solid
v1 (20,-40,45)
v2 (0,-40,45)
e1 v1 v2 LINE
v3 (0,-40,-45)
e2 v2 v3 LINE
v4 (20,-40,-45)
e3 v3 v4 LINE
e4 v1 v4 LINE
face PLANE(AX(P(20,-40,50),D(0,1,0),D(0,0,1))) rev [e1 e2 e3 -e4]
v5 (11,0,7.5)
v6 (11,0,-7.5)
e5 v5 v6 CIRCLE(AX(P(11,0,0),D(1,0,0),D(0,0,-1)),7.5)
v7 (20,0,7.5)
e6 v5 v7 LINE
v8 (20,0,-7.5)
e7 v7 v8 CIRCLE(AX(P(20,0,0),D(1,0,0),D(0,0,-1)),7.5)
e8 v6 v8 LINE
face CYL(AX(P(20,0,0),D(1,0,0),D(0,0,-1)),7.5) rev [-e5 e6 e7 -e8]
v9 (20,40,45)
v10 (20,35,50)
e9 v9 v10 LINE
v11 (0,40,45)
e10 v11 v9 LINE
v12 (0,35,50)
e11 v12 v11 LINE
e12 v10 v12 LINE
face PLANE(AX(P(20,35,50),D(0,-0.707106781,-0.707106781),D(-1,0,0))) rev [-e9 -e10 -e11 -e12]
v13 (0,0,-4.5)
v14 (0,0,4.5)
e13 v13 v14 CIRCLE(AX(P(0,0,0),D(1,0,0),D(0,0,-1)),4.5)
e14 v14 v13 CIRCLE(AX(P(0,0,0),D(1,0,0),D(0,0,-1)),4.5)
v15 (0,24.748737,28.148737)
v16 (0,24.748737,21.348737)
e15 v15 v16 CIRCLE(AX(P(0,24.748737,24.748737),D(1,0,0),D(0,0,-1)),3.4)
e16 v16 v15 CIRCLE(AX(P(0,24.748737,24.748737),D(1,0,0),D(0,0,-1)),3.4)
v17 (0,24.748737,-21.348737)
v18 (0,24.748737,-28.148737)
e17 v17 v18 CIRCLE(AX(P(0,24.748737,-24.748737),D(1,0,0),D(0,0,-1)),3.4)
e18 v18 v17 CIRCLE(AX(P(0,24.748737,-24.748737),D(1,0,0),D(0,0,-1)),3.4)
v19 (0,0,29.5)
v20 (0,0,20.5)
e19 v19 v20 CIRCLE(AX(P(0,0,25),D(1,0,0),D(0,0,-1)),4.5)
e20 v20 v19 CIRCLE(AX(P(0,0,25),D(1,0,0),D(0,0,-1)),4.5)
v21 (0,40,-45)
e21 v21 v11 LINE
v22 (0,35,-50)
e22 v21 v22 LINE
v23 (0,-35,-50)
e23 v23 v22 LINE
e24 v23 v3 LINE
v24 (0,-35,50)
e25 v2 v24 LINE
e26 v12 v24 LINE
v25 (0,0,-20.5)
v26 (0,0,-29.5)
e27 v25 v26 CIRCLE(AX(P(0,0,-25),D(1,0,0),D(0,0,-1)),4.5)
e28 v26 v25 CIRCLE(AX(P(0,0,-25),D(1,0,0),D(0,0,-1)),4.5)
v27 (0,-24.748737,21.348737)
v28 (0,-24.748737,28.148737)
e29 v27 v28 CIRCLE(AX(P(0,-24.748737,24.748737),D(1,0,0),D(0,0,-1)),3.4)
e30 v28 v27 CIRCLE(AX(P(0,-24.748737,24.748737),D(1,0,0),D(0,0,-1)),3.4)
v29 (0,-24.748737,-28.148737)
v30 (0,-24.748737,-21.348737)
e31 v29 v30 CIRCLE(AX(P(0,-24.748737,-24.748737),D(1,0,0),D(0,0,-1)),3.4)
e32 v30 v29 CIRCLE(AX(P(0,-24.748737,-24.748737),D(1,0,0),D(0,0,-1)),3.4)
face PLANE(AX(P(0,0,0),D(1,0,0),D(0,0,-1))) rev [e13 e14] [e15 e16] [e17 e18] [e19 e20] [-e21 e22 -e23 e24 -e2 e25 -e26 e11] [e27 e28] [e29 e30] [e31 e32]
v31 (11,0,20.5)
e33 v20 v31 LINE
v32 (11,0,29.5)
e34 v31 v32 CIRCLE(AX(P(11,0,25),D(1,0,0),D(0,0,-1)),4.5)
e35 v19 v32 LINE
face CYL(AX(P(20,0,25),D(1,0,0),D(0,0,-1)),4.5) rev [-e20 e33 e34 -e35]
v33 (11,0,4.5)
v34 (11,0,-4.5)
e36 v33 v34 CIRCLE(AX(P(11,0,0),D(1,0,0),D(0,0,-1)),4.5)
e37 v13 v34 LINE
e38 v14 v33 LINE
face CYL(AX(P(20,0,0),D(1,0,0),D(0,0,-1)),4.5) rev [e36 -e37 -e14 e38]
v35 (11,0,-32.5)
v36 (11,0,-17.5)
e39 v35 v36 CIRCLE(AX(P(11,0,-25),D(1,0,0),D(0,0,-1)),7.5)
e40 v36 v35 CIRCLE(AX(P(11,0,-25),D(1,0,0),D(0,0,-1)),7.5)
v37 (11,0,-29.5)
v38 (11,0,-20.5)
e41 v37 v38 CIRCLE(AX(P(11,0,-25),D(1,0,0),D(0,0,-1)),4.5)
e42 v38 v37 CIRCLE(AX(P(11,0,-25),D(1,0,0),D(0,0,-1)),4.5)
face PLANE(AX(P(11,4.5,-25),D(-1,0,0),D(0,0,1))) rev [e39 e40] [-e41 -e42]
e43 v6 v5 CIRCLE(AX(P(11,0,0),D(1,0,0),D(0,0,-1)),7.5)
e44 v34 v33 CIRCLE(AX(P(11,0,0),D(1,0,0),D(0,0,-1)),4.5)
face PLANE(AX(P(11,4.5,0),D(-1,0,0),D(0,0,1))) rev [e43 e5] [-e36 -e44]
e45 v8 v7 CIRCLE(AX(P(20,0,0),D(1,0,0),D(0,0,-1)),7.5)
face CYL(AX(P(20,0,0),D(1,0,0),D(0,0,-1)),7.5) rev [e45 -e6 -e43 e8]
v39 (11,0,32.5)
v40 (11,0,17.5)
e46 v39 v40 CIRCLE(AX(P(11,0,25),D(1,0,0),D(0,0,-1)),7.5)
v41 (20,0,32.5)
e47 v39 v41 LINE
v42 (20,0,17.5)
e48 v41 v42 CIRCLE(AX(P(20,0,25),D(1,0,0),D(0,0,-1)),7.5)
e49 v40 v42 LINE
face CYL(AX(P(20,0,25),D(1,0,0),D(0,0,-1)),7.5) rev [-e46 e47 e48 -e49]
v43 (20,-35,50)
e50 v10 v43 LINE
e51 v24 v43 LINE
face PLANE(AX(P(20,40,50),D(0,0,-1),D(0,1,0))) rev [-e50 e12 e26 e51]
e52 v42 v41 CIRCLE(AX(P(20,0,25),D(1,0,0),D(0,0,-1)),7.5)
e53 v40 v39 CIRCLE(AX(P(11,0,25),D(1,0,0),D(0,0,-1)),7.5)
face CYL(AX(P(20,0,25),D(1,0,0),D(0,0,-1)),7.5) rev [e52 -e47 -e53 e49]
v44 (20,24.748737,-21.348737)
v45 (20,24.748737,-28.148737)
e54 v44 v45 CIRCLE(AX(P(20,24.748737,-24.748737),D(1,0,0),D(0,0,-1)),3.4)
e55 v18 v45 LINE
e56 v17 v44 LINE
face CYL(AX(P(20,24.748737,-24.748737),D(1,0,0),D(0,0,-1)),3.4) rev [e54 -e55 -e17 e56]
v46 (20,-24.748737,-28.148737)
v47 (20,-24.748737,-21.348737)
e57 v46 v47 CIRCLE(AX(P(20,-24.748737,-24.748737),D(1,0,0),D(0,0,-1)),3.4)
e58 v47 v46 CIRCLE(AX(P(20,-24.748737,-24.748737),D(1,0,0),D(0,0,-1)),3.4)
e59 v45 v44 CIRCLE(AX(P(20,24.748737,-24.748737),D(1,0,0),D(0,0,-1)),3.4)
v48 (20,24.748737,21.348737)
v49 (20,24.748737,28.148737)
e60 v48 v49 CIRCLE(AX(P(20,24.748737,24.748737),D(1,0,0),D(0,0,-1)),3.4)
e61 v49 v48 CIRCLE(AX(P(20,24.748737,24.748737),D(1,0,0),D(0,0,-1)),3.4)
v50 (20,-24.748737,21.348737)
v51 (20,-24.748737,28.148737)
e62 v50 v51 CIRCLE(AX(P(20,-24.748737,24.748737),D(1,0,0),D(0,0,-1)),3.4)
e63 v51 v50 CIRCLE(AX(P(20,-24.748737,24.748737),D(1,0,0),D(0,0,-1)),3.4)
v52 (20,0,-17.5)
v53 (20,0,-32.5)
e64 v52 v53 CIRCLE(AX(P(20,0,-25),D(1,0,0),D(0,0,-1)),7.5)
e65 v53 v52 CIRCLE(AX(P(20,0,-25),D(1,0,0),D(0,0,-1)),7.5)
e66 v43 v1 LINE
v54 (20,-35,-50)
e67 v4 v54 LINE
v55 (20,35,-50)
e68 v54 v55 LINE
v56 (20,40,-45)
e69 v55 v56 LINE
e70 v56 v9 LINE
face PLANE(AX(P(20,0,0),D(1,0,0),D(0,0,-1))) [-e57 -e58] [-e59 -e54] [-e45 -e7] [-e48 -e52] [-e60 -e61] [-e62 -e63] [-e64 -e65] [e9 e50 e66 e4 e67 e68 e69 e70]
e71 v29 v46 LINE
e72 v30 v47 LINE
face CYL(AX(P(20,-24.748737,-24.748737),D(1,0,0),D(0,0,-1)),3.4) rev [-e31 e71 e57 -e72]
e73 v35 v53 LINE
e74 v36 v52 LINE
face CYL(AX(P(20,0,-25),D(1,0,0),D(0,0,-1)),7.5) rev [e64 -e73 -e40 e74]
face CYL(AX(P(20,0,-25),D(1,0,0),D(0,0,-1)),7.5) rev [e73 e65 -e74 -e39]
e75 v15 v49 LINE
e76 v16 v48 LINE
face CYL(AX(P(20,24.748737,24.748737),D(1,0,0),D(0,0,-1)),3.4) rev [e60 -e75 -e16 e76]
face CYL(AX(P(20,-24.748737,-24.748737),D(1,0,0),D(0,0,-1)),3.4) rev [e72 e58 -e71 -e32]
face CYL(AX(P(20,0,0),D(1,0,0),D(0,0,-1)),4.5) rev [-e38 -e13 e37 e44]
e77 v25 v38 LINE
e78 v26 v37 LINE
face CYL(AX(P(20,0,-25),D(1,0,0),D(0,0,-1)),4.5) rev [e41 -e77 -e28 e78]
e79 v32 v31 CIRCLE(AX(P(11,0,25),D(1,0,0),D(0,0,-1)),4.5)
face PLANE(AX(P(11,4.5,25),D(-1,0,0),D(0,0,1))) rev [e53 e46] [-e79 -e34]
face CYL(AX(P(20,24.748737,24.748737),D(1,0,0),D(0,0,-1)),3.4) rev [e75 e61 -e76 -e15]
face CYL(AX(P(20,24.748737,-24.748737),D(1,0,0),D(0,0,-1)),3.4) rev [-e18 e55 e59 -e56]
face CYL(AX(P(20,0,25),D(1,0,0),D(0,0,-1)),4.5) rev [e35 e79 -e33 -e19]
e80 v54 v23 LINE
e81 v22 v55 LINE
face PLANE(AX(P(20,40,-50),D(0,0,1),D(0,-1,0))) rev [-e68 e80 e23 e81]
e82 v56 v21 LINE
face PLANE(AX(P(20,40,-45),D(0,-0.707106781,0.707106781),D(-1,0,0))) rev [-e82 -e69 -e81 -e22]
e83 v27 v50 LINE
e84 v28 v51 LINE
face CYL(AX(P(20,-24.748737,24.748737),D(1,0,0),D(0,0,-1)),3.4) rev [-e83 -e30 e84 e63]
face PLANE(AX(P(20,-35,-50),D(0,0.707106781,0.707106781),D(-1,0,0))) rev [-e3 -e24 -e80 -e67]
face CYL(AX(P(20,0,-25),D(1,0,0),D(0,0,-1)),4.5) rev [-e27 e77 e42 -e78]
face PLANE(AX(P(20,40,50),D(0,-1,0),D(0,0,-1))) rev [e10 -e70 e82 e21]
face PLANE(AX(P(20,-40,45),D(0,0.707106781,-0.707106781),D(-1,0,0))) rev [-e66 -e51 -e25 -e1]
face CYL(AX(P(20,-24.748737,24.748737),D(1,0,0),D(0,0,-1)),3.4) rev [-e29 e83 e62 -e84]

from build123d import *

# Parameters (mm, degrees)
SKETCH_1_W                = 100
SKETCH_1_H                = 80
EXTRUDE_1_DEPTH           = 20
HOLE_WIZARD_M8_1_D        = 6.8
HOLE_WIZARD_1_D           = 9
HOLE_WIZARD_1_CBORE_D     = 15
HOLE_WIZARD_1_CBORE_DEPTH = 9
CHAMFER_1_SIZE            = 5


with BuildPart() as part:
    # 草图1 → 凸台-拉伸1 (new body)
    with BuildSketch(Plane(origin=(0, 0, 0), x_dir=(0, 0, -1), z_dir=(1, 0, 0))):
        Rectangle(SKETCH_1_W, SKETCH_1_H)
    extrude(amount=EXTRUDE_1_DEPTH)

    # M8 螺纹孔1 (through all)
    with Locations(Plane(origin=(20, 0, 0), x_dir=(0, 0, -1), z_dir=(1, 0, 0))):
        with Locations((-24.748737342, 24.748737342), (24.748737342, 24.748737342), (24.748737342, -24.748737342), (-24.748737342, -24.748737342)):
            Hole(HOLE_WIZARD_M8_1_D / 2)

    # 打孔尺寸(%根据)内六角圆柱头螺钉的类型1 (through all)
    with Locations(Plane(origin=(20, 0, 0), x_dir=(0, 0, -1), z_dir=(1, 0, 0))):
        with Locations((-25, 0), (0, 0), (25, 0)):
            CounterBoreHole(HOLE_WIZARD_1_D / 2, HOLE_WIZARD_1_CBORE_D / 2, HOLE_WIZARD_1_CBORE_DEPTH)

    # 倒角1
    chamfer_1_edges = [part.edges().sort_by_distance(p)[0] for p in [
        (10, -40, -50),
        (10, -40, 50),
        (10, 40, 50),
        (10, 40, -50),
    ]]
    chamfer(chamfer_1_edges, length=CHAMFER_1_SIZE)


solid = part.part
